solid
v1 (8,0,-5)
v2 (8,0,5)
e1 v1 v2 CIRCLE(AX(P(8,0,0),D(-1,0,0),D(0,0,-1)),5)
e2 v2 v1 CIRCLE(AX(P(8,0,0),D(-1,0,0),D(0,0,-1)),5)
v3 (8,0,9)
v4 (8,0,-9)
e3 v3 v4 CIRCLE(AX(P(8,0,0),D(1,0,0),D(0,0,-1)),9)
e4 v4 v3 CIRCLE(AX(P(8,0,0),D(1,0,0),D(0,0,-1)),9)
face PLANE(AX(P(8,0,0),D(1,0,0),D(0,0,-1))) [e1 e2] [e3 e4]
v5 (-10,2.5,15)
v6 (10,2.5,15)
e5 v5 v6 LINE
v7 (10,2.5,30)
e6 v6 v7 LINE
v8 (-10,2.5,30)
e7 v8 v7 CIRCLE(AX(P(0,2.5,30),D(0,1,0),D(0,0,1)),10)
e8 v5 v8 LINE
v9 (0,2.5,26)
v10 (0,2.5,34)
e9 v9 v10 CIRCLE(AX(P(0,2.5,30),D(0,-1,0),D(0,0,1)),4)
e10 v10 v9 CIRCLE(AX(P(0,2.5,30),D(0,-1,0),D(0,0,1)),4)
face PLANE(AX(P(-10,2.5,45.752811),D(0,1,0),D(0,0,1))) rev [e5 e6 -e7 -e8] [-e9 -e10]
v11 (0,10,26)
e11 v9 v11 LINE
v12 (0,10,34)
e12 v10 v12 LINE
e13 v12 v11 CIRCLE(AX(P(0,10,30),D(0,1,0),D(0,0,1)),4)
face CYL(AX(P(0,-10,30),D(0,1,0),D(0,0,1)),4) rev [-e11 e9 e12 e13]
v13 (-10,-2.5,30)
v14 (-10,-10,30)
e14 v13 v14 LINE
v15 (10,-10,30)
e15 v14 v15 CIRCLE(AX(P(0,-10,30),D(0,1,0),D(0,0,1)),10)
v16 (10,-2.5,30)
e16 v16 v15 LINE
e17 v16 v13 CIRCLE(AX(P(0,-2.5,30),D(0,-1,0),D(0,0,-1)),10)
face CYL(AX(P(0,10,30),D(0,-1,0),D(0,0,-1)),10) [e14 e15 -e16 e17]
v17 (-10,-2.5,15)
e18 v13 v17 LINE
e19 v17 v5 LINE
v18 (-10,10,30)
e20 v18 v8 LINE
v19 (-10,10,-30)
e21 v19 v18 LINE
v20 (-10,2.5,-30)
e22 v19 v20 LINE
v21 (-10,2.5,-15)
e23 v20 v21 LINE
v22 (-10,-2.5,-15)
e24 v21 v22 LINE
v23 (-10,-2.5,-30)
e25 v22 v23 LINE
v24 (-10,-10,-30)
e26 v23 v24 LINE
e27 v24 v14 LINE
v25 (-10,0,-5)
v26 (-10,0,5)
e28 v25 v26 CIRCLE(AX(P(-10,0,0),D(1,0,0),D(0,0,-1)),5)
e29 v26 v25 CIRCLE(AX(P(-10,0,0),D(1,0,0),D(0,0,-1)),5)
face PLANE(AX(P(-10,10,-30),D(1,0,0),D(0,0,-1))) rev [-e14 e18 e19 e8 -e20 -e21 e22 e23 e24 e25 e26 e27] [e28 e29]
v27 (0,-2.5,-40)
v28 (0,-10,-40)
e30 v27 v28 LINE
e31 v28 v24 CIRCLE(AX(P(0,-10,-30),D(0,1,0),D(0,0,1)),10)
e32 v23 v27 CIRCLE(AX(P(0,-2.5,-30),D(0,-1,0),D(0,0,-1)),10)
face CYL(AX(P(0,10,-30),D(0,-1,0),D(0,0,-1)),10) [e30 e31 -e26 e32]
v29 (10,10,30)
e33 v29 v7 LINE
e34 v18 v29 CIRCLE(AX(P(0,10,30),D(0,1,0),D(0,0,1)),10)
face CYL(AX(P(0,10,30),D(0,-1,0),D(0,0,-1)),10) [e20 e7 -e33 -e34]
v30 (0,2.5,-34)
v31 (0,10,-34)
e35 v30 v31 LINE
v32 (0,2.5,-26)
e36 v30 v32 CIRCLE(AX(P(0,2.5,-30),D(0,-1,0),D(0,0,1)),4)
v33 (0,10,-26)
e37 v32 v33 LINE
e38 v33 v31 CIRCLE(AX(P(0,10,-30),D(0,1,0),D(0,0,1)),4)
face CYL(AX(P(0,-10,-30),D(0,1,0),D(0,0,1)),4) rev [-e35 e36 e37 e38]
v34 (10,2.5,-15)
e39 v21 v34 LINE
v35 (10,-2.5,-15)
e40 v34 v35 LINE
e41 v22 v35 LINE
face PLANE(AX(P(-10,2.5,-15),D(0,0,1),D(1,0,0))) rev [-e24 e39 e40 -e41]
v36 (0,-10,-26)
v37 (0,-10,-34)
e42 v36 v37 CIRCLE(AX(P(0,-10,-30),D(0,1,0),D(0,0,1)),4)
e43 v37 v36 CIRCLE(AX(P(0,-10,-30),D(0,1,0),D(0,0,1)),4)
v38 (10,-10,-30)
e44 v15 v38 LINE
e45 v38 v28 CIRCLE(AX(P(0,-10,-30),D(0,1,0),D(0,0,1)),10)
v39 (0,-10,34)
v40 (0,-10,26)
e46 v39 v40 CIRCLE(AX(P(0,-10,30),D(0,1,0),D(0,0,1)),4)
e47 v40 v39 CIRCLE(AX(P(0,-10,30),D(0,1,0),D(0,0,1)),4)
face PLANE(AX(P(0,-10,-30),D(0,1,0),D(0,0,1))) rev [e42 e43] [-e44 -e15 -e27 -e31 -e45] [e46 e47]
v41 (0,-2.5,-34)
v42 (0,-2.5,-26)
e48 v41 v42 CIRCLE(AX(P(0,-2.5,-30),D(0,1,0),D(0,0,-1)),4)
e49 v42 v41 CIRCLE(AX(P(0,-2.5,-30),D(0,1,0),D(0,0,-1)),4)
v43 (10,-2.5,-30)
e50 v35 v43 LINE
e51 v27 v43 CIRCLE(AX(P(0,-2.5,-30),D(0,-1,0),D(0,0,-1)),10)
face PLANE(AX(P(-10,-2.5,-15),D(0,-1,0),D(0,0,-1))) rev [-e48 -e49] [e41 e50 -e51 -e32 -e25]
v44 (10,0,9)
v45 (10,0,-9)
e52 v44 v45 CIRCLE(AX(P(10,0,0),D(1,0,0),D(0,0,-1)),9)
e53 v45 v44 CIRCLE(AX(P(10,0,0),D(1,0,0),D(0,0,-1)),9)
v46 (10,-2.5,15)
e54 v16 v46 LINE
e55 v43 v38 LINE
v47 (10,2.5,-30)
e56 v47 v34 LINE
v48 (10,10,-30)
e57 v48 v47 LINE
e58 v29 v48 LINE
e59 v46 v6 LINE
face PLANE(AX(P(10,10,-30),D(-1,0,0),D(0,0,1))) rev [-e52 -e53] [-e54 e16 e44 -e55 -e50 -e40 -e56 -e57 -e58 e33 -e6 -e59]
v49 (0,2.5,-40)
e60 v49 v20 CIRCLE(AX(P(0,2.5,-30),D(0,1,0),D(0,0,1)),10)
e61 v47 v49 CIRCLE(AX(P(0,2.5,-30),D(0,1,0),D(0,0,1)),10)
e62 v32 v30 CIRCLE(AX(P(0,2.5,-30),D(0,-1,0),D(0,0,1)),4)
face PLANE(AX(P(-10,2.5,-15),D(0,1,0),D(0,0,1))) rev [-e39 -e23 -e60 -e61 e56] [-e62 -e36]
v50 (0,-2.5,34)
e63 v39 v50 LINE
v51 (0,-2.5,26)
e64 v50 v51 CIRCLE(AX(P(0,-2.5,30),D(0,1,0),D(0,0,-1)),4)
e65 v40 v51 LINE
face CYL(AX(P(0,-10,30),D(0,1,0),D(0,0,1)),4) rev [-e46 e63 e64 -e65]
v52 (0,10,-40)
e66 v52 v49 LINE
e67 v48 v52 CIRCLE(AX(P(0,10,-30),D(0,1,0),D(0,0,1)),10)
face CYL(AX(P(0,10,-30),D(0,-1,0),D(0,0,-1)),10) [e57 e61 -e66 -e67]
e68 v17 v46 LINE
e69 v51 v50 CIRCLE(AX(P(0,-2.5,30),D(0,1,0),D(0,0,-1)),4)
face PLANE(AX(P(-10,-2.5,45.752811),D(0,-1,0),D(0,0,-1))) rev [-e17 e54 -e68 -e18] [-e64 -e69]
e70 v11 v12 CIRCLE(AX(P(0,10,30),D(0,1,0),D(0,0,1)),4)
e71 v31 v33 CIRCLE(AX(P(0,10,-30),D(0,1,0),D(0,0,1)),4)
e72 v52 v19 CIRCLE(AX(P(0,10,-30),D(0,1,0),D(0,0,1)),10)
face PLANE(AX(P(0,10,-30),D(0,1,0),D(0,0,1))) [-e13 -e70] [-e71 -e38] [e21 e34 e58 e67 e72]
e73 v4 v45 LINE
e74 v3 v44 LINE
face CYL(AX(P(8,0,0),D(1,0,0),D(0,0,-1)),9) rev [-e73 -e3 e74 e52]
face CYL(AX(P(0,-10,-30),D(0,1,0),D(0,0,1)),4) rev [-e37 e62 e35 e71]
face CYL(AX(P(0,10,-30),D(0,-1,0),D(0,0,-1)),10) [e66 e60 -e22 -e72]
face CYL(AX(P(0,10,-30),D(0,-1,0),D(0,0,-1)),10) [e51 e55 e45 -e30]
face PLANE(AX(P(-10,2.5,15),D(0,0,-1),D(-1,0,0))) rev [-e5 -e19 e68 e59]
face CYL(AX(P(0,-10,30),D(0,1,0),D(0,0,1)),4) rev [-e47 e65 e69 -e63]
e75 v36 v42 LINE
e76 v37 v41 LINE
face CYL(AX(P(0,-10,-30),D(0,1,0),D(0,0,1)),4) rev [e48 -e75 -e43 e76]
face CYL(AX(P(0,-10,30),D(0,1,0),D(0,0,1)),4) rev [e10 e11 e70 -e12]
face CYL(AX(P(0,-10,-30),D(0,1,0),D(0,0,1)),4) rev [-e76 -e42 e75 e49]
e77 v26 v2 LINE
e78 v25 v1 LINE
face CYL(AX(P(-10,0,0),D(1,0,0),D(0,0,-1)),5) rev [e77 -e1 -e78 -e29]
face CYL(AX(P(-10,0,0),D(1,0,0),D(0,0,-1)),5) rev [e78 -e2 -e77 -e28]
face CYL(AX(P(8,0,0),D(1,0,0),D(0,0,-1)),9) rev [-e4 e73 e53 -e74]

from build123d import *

# Parameters (mm, degrees)
LINK_BODY_DEPTH        = 10
PIN_HOLES_SKETCH_R     = 4
PIN_HOLES_2X_8_DEPTH   = 10
SIDE_SLOTS_SKETCH_R    = 5
SIDE_SLOTS_SKETCH_W    = 30.75281097
SIDE_SLOTS_SKETCH_H    = 5
SIDE_SLOTS_SKETCH_W_2  = 29.537366276
SIDE_SLOTS_CUT_DEPTH   = 10
COUNTERBORE_SKETCH_R   = 9
COUNTERBORE_18X2_DEPTH = 2


with BuildPart() as part:
    # Link Body Sketch → Link Body (new, symmetric)
    with BuildSketch(Plane(origin=(0, 0, 0), x_dir=(1, 0, 0), z_dir=(0, 1, 0))):
        with BuildLine():
            Line((10, 30), (10, -30))
            ThreePointArc((10, -30), (0, -40), (-10, -30))
            Line((-10, -30), (-10, 30))
            ThreePointArc((-10, 30), (0, 40), (10, 30))
        make_face()
    extrude(amount=LINK_BODY_DEPTH, both=True)

    # Pin Holes Sketch → Pin Holes 2xØ8 (cut, symmetric)
    with BuildSketch(Plane(origin=(0, 0, 0), x_dir=(1, 0, 0), z_dir=(0, 1, 0))):
        with Locations(Location((0, 30, 0), (0, 0, 270))):
            Circle(PIN_HOLES_SKETCH_R)
        with Locations(Location((0, -30, 0), (0, 0, 270))):
            Circle(PIN_HOLES_SKETCH_R)
    extrude(amount=PIN_HOLES_2X_8_DEPTH, both=True, mode=Mode.SUBTRACT)

    # Side Slots Sketch → Side Slots Cut (cut, symmetric)
    with BuildSketch(Plane(origin=(0, 0, 0), x_dir=(0, 0, -1), z_dir=(1, 0, 0))):
        Circle(SIDE_SLOTS_SKETCH_R)
        with Locations((-30.376405485, 0)):
            Rectangle(SIDE_SLOTS_SKETCH_W, SIDE_SLOTS_SKETCH_H)
        with Locations((29.768683138, 0)):
            Rectangle(SIDE_SLOTS_SKETCH_W_2, SIDE_SLOTS_SKETCH_H)
    extrude(amount=SIDE_SLOTS_CUT_DEPTH, both=True, mode=Mode.SUBTRACT)

    # Counterbore Sketch → Counterbore Ø18x2 (cut)
    with BuildSketch(Plane(origin=(10, 0, 0), x_dir=(0, 0, -1), z_dir=(1, 0, 0))):
        Circle(COUNTERBORE_SKETCH_R)
    extrude(amount=-COUNTERBORE_18X2_DEPTH, mode=Mode.SUBTRACT)


solid = part.part
